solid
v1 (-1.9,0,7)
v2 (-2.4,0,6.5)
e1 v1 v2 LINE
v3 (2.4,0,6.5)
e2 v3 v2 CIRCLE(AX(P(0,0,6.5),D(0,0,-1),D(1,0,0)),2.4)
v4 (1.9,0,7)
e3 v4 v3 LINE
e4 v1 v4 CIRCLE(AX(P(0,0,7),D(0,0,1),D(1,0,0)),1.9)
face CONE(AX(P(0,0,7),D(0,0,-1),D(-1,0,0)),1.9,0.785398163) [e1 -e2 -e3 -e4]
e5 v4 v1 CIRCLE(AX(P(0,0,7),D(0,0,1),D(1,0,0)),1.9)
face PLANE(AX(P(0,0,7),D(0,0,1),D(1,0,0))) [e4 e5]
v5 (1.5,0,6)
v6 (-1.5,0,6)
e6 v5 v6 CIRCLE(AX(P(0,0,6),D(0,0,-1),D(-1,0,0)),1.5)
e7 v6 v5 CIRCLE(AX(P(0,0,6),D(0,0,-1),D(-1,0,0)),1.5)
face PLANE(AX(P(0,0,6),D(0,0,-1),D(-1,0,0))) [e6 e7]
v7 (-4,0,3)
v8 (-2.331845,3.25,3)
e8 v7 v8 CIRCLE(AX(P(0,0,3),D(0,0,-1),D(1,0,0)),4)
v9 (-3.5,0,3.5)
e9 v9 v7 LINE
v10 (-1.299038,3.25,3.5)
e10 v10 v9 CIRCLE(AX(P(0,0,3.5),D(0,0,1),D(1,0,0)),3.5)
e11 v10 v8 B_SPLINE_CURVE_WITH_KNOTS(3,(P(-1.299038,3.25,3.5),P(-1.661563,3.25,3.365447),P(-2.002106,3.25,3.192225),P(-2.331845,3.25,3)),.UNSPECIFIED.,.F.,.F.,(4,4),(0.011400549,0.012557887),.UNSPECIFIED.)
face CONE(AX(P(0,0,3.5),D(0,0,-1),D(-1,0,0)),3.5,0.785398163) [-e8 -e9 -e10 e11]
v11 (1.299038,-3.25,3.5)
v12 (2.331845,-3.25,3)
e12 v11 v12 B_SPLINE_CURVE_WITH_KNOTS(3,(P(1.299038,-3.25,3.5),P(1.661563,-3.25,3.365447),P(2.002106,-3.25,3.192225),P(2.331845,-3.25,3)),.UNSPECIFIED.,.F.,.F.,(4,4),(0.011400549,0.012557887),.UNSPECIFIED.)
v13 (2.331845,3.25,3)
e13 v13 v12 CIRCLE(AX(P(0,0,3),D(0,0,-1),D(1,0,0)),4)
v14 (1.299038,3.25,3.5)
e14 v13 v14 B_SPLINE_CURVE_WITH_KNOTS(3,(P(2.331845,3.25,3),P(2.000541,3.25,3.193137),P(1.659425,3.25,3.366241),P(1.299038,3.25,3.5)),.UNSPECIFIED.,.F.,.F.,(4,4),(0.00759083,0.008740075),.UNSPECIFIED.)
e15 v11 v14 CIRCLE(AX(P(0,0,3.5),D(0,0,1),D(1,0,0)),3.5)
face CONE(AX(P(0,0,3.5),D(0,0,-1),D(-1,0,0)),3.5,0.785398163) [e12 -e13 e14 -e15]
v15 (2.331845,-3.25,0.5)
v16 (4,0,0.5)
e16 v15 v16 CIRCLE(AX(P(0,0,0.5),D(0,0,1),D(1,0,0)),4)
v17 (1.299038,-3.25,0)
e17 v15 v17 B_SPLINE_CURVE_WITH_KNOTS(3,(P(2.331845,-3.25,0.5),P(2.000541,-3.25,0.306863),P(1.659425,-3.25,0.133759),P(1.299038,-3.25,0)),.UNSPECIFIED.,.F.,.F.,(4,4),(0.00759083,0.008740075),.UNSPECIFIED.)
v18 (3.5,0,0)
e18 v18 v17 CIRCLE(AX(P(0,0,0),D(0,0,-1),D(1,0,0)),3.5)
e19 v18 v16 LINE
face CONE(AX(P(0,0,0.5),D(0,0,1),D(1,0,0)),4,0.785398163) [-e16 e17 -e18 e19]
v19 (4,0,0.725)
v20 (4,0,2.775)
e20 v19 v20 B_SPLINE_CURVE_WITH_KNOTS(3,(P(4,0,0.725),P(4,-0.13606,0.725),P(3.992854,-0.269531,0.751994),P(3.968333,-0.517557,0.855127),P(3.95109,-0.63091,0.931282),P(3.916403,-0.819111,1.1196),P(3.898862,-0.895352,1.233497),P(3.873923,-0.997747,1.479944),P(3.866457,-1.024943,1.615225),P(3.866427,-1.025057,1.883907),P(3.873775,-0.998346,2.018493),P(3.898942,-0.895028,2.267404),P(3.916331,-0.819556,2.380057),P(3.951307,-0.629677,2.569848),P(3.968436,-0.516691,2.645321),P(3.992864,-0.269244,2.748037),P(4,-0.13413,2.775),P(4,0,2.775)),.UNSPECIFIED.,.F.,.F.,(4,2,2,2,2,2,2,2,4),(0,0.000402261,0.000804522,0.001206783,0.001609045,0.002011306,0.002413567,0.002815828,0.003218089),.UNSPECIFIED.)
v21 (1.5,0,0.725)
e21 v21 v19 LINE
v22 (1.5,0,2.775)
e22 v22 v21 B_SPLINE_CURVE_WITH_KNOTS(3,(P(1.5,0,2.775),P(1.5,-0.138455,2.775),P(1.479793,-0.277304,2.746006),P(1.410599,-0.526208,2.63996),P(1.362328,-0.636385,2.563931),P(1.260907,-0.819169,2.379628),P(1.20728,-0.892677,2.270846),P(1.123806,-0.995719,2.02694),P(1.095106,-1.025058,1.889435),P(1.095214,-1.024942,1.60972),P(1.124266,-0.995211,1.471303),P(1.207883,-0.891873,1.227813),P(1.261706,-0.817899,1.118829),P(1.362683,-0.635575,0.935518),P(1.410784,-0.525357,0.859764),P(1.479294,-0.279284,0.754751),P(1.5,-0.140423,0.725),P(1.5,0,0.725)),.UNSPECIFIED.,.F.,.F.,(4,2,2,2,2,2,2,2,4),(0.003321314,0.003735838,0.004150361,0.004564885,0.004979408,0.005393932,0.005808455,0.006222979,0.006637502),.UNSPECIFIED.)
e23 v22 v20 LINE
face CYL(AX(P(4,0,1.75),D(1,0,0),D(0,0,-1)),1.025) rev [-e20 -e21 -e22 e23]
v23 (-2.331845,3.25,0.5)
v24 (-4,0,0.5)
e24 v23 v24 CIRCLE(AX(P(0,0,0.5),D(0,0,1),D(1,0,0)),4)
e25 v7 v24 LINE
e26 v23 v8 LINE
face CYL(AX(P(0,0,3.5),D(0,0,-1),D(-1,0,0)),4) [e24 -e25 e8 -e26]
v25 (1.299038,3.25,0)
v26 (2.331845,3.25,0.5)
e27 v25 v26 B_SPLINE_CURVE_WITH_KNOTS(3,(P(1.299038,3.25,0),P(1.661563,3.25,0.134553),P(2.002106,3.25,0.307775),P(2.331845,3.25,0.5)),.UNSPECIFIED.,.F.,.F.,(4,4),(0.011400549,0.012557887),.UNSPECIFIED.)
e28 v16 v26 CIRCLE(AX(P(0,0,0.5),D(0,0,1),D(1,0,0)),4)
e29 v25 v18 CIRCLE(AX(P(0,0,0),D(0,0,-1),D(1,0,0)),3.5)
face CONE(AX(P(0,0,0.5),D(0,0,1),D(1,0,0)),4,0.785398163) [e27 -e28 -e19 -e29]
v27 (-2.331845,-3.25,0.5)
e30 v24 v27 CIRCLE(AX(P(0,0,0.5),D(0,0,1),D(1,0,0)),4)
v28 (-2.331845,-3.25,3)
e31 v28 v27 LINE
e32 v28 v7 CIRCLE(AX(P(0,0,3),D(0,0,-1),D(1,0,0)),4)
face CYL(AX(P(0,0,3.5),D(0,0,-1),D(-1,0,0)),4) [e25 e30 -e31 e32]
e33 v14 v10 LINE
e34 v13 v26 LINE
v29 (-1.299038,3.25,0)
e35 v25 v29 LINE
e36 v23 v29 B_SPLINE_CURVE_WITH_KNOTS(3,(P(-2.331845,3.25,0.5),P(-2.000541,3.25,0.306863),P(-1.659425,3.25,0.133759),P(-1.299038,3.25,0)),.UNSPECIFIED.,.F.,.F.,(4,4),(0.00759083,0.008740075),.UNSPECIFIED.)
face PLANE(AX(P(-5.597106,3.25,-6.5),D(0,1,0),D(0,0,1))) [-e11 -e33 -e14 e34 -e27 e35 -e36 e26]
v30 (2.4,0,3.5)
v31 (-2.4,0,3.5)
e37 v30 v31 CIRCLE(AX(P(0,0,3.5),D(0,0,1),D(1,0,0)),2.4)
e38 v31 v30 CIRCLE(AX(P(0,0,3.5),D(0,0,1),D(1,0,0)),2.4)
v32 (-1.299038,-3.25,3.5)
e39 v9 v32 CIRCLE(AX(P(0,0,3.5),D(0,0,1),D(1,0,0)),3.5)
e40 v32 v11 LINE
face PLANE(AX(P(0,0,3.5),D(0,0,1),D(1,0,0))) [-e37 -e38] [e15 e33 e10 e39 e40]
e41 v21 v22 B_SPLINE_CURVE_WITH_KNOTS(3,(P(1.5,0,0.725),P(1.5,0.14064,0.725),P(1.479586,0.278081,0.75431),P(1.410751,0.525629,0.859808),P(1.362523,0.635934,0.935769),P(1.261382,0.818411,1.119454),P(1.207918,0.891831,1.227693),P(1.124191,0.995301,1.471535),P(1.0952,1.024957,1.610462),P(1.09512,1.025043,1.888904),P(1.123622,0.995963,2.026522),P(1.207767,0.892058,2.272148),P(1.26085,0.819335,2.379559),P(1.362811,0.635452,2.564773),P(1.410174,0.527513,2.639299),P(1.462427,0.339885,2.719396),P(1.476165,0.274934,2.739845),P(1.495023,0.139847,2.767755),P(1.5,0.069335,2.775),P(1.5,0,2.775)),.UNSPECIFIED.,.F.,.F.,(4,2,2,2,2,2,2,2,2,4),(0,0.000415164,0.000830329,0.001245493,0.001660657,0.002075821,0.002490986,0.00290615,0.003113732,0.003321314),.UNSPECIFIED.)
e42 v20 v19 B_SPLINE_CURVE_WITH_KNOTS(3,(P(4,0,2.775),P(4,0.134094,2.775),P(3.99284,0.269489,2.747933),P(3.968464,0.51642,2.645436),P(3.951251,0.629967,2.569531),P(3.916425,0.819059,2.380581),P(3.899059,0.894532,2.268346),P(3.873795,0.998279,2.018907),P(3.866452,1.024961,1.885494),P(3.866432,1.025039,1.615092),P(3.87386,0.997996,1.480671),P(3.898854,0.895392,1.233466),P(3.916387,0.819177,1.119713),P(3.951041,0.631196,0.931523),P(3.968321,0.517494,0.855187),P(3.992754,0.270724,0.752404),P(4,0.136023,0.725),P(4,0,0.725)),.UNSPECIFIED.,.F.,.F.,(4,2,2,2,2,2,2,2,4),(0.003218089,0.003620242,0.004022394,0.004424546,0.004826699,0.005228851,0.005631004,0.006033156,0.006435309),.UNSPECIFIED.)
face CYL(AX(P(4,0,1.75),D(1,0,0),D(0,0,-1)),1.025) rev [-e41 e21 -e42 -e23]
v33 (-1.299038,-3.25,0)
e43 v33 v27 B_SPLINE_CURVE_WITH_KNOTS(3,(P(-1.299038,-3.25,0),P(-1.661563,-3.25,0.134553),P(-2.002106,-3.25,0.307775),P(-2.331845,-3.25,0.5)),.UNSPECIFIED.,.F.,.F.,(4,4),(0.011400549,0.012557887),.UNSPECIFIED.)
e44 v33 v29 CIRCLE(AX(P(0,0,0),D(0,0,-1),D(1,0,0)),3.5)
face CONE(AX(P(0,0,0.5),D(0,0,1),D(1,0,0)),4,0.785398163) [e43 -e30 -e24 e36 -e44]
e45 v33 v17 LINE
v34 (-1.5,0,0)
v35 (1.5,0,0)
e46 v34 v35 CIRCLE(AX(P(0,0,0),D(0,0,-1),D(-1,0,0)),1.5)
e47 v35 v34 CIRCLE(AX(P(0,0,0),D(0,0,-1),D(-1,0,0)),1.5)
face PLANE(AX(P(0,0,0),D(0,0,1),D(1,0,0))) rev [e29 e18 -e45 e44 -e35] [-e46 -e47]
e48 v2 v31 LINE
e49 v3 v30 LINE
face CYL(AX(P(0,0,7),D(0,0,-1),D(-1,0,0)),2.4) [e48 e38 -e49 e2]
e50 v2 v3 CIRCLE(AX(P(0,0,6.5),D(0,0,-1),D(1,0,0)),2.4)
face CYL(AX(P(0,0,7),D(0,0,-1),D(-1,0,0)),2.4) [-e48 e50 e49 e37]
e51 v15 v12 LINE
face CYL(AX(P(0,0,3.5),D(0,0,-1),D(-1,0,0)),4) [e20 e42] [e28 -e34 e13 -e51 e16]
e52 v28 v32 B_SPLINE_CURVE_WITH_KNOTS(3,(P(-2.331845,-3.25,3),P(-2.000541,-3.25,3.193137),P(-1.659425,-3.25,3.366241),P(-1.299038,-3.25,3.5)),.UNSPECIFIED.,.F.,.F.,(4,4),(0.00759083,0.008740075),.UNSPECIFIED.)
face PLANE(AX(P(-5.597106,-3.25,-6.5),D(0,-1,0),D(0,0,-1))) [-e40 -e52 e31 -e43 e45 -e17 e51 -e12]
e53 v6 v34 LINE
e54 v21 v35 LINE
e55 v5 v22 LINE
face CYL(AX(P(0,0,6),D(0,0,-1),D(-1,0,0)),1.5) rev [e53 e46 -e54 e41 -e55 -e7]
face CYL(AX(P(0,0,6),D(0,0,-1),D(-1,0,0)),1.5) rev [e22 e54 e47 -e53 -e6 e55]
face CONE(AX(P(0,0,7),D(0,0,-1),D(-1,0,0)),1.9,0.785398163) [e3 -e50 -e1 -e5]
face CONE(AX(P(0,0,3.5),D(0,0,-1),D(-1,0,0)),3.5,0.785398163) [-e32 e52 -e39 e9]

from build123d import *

# Parameters (mm, degrees)
SKETCH1_R                = 4
BOSS_EXTRUDE1_DEPTH      = 3.5
SKETCH3_R                = 2.4
BOSS_EXTRUDE2_DEPTH      = 3.5
SKETCH2_R                = 1.5
CUT_EXTRUDE1_DEPTH       = 6
M2_5_TAPPED_HOLE1_REACH  = 13.358
M2_5_TAPPED_HOLE1_BORE_R = 1.025
CHAMFER1_SIZE            = 0.5
SKETCH6_OUTSIDE_W        = 12.66
SKETCH6_OUTSIDE_H        = 12.66
SKETCH6_OUTSIDE_W_2      = 11.194211724
SKETCH6_OUTSIDE_H_2      = 6.5
CUT_EXTRUDE2_DEPTH       = 10


with BuildPart() as part:
    # Sketch1 → Boss-Extrude1 (new body)
    with BuildSketch(Plane.XY):
        Circle(SKETCH1_R)
    extrude(amount=BOSS_EXTRUDE1_DEPTH)

    # Sketch3 → Boss-Extrude2 (add)
    with BuildSketch(Plane.XY.offset(3.5)):
        Circle(SKETCH3_R)
    extrude(amount=BOSS_EXTRUDE2_DEPTH)

    # Sketch2 → Cut-Extrude1 (cut)
    with BuildSketch(Plane(origin=(0, 0, 0), x_dir=(-1, 0, 0), z_dir=(0, 0, -1))):
        Circle(SKETCH2_R)
    extrude(amount=-CUT_EXTRUDE1_DEPTH, mode=Mode.SUBTRACT)

    # M2.5 Tapped Hole1 bore → M2.5 Tapped Hole1 (cut, up to next)
    with BuildSketch(Plane(origin=(4, 0, 0), x_dir=(0, 0, -1), z_dir=(1, 0, 0)), mode=Mode.PRIVATE) as m2_5_tapped_hole1_sk1:
        with Locations((-1.75, 0)):
            Circle(M2_5_TAPPED_HOLE1_BORE_R)
    m2_5_tapped_hole1_tool1 = extrude(m2_5_tapped_hole1_sk1.sketch, amount=-M2_5_TAPPED_HOLE1_REACH, mode=Mode.PRIVATE) & part.part
    add(m2_5_tapped_hole1_tool1.solids().sort_by_distance((4, 0, 1.75))[0], mode=Mode.SUBTRACT)

    # Chamfer1
    chamfer1_edges = [part.edges().sort_by_distance(p)[0] for p in [
        (-4, 0, 0),
        (-4, 0, 3.5),
        (-2.4, 0, 7),
    ]]
    chamfer(chamfer1_edges, length=CHAMFER1_SIZE)

    # Sketch6 outside → Cut-Extrude2 (cut)
    with BuildSketch(Plane.XY.offset(3.5)):
        Rectangle(SKETCH6_OUTSIDE_W, SKETCH6_OUTSIDE_H)
        Rectangle(SKETCH6_OUTSIDE_W_2, SKETCH6_OUTSIDE_H_2, mode=Mode.SUBTRACT)
    extrude(amount=-CUT_EXTRUDE2_DEPTH, mode=Mode.SUBTRACT)


solid = part.part
